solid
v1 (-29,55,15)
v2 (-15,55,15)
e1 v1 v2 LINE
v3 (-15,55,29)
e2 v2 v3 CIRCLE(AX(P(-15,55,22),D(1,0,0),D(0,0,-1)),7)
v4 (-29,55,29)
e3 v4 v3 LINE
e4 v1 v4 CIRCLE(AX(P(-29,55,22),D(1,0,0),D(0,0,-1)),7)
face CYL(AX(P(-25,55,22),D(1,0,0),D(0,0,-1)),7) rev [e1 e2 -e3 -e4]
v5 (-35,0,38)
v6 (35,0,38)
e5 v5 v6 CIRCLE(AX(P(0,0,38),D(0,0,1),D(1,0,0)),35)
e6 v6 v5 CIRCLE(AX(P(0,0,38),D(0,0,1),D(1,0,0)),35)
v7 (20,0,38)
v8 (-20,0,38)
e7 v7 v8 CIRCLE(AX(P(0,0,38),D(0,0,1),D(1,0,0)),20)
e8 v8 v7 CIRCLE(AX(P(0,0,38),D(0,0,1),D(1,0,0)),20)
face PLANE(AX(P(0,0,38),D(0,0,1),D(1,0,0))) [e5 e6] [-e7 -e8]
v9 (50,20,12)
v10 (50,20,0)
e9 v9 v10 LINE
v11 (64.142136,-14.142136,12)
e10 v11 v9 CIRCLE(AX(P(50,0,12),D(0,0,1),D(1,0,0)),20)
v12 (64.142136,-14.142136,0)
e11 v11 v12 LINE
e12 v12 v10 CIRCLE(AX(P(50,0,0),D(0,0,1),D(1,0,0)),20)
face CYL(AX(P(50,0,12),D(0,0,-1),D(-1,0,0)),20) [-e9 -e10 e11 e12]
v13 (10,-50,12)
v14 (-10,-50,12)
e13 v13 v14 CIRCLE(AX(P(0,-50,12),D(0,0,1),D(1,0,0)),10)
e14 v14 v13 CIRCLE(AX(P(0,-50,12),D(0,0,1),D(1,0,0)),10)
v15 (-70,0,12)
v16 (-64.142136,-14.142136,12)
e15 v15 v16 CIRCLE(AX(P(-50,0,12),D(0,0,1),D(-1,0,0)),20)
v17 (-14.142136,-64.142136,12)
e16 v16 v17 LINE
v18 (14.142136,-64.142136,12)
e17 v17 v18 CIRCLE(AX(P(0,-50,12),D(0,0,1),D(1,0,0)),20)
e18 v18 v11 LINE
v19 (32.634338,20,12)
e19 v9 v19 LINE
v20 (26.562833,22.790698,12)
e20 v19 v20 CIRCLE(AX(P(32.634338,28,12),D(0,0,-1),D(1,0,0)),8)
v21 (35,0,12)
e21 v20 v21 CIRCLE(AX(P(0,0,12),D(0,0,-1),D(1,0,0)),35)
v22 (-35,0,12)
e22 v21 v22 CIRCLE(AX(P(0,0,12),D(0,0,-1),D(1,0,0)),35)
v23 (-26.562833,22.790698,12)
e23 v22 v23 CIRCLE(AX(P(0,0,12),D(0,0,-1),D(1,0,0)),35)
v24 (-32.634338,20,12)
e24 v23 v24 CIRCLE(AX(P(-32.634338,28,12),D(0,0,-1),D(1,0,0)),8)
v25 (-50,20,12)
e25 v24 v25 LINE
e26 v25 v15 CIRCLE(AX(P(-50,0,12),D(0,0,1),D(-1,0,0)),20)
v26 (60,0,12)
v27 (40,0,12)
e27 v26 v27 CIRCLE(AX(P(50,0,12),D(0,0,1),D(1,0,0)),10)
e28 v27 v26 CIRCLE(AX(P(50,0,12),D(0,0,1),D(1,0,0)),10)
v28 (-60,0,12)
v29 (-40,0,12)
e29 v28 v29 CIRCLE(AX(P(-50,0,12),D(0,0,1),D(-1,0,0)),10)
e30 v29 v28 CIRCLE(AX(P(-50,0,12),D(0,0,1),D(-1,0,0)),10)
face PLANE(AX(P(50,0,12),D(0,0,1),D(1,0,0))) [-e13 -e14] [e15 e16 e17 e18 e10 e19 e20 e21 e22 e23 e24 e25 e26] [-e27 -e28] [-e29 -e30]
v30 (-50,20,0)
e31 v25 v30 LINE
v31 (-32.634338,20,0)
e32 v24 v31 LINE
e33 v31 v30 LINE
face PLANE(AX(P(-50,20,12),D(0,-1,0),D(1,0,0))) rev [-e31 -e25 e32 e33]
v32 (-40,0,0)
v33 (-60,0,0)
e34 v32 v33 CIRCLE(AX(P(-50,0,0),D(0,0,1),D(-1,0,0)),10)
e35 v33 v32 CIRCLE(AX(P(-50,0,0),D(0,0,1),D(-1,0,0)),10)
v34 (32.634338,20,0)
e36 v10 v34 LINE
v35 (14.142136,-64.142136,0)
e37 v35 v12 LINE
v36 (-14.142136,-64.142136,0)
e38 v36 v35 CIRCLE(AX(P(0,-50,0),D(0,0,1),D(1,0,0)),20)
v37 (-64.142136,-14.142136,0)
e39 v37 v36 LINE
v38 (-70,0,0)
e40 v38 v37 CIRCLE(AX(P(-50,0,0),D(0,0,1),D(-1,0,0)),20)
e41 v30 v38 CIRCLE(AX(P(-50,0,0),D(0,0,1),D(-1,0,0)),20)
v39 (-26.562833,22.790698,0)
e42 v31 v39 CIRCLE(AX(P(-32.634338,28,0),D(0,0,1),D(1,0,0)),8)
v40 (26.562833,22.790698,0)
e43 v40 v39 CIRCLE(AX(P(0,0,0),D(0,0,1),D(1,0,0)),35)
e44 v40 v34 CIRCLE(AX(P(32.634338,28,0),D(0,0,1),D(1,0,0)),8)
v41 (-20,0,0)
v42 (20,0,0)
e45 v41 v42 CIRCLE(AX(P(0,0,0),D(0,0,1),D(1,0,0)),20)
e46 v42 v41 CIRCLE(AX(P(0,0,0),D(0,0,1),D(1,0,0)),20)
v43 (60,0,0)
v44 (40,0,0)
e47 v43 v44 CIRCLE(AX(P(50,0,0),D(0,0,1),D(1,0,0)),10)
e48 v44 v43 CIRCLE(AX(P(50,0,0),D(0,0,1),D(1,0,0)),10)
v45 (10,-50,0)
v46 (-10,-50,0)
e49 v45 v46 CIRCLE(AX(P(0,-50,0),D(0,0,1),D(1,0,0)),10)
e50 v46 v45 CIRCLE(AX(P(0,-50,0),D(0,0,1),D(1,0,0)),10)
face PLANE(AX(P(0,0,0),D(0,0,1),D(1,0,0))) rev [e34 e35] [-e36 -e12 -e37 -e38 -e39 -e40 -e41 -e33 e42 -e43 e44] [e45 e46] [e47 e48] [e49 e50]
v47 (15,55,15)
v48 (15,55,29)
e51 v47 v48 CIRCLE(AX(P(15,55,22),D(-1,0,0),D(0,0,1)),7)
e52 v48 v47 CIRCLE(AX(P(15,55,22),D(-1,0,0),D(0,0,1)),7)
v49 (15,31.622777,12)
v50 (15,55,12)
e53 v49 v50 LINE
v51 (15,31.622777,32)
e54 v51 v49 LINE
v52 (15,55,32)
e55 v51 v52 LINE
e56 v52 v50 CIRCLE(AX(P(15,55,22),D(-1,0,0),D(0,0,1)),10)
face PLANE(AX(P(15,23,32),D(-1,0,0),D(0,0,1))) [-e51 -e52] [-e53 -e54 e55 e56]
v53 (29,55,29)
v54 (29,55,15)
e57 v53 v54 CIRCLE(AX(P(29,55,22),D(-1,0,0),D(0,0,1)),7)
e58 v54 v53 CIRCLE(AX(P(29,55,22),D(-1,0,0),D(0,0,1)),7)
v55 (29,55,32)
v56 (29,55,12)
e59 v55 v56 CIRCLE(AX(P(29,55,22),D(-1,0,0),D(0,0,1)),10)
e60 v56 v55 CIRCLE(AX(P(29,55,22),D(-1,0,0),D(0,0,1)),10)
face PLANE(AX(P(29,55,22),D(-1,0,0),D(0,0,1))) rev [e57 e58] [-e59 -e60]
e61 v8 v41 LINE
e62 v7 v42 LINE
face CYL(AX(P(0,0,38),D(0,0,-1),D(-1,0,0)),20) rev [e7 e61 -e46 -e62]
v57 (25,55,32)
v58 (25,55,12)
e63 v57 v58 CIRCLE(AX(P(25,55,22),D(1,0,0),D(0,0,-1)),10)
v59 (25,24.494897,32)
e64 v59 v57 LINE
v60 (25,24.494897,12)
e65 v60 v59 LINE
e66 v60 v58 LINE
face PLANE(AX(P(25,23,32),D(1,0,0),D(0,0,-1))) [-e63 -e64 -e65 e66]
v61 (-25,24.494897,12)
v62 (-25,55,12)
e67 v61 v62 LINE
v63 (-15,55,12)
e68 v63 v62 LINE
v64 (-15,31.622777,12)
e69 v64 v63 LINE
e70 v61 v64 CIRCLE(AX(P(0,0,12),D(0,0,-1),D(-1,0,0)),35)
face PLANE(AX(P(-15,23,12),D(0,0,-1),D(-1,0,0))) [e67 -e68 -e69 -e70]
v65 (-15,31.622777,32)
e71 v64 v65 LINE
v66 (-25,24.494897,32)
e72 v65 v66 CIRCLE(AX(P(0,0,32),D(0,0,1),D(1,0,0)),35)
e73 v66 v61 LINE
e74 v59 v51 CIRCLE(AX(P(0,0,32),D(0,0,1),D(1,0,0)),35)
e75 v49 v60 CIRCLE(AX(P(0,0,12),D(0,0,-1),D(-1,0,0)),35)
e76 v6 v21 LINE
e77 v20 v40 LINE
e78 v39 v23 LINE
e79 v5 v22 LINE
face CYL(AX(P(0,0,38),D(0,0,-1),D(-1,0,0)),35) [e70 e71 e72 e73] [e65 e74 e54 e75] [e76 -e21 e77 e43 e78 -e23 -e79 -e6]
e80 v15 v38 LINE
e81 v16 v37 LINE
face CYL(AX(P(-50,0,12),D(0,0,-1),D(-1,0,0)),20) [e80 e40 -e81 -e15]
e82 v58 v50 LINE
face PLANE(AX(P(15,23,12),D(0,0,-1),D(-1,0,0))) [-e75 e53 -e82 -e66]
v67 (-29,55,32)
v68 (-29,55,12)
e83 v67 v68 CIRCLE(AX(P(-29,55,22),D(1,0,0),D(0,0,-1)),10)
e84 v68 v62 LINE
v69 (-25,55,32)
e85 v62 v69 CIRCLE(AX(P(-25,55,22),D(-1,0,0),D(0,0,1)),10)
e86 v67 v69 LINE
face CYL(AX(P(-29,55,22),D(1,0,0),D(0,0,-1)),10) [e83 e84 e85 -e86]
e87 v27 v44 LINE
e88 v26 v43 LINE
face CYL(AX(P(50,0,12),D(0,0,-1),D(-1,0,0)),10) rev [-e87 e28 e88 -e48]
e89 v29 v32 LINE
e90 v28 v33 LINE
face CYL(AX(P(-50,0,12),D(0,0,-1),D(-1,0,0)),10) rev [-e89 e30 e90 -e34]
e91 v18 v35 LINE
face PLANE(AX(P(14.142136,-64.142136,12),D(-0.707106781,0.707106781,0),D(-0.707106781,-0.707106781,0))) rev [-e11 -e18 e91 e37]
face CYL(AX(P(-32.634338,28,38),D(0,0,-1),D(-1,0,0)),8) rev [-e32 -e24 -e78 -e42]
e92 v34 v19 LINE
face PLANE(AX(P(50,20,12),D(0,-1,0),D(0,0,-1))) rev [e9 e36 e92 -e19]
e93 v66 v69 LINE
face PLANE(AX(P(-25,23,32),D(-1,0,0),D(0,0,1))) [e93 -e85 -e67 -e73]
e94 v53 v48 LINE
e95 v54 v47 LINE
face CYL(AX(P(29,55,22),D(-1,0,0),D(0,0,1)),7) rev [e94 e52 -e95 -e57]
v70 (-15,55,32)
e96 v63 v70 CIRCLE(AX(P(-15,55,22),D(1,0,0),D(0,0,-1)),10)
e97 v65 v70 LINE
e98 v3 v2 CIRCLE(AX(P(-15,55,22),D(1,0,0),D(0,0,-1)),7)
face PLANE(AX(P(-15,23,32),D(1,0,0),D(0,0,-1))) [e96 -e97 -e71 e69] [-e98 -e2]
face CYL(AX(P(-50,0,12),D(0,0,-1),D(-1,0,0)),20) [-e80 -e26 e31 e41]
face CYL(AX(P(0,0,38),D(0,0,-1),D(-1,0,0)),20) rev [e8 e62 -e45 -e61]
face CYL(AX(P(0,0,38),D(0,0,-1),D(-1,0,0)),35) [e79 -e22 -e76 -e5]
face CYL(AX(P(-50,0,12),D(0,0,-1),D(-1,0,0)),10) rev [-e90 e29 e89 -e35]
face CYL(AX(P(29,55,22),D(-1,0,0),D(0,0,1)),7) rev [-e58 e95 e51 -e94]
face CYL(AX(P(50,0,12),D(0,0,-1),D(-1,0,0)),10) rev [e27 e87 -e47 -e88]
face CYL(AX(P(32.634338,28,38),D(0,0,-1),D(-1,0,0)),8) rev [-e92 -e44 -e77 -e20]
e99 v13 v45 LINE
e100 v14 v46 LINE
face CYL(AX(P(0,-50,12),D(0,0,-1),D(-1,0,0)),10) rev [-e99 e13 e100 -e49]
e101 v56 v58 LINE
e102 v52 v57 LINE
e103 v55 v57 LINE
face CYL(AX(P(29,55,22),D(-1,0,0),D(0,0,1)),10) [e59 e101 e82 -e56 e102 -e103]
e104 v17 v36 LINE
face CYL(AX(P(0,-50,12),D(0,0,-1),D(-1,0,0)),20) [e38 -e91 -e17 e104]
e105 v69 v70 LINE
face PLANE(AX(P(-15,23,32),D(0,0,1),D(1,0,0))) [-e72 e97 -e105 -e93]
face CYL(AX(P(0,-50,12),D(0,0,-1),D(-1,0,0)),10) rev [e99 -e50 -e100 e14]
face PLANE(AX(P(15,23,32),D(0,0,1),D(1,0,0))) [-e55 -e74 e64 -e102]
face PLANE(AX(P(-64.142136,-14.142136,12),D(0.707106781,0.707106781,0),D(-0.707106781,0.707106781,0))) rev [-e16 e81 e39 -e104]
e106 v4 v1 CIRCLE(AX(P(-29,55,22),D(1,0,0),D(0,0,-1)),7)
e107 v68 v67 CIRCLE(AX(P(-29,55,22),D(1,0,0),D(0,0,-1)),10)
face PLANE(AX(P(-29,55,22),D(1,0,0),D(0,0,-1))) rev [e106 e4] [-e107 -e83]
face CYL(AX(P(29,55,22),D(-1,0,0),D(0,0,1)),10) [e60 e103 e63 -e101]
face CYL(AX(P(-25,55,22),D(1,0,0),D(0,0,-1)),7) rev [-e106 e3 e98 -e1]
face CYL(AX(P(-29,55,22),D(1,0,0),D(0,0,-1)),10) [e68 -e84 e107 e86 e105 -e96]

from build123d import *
from build123d.topology import SkipClean

# Parameters (mm, degrees)
HUB_PROFILE_SKETCH_R     = 35
HUB_PROFILE_SKETCH_R_2   = 20
HUB_70_BORE_40_DEPTH     = 38
MOUNTING_FLANGE_SKETCH_R = 10
MOUNTING_FLANGE_DEPTH    = 12
FLANGE_HUB_FILLET_R8_R   = 8
CLEVIS_LUG_SKETCH_W      = 10
CLEVIS_LUG_SKETCH_H      = 20
CLEVIS_LUGS_DEPTH        = 32
LUG_BOSS_SKETCH_A_R      = 10
LUG_BOSS_SKETCH_A_R_2    = 7
LUG_BOSS_A_20_DEPTH      = 14
PIN_START                = -50
PIN_HOLE_SKETCH_R        = 7
PIN_HOLE_14_DEPTH        = 50
LUG_START                = -14
LUG_BOSS_SKETCH_B_R      = 10
LUG_BOSS_SKETCH_B_R_2    = 7
LUG_BOSS_B_20_DEPTH      = 14


with BuildPart() as part:
    # Hub Profile Sketch → Hub Ø70 Bore Ø40 (new body)
    with BuildSketch(Plane.XY):
        Circle(HUB_PROFILE_SKETCH_R)
        Circle(HUB_PROFILE_SKETCH_R_2, mode=Mode.SUBTRACT)
    extrude(amount=HUB_70_BORE_40_DEPTH)

    # Mounting Flange Sketch → Mounting Flange (add)
    with BuildSketch(Plane.XY):
        with BuildLine():
            Line((50, 20), (28.722813233, 20))
            ThreePointArc((28.722813233, 20), (0, -35), (-28.722813233, 20))
            Line((-28.722813233, 20), (-50, 20))
            ThreePointArc((-50, 20), (-68.47759065, 7.653668647), (-64.142135624, -14.142135624))
            Line((-64.142135624, -14.142135624), (-14.142135624, -64.142135624))
            ThreePointArc((-14.142135624, -64.142135624), (0, -70), (14.142135624, -64.142135624))
            Line((14.142135624, -64.142135624), (64.142135624, -14.142135624))
            ThreePointArc((64.142135624, -14.142135624), (68.47759065, 7.653668647), (50, 20))
        make_face()
        with Locations((50, 0)):
            Circle(MOUNTING_FLANGE_SKETCH_R, mode=Mode.SUBTRACT)
        with Locations((0, -50)):
            Circle(MOUNTING_FLANGE_SKETCH_R, mode=Mode.SUBTRACT)
        with Locations(Location((-50, 0, 0), (0, 0, 180))):
            Circle(MOUNTING_FLANGE_SKETCH_R, mode=Mode.SUBTRACT)
    extrude(amount=MOUNTING_FLANGE_DEPTH)

    # Flange Hub Fillet R8
    flange_hub_fillet_r8_edges = [part.edges().sort_by_distance(p)[0] for p in [
        (28.722813233, 20, 6),
        (-28.722813233, 20, 6),
    ]]
    fillet(flange_hub_fillet_r8_edges, radius=FLANGE_HUB_FILLET_R8_R)

    # Clevis Lug Sketch → Clevis Lugs (add)
    with BuildSketch(Plane(origin=(0, 55, 0), x_dir=(1, 0, 0), z_dir=(0, 1, 0))):
        with Locations((-20, -22)):
            Rectangle(CLEVIS_LUG_SKETCH_W, CLEVIS_LUG_SKETCH_H)
        with Locations((20, -22)):
            Rectangle(CLEVIS_LUG_SKETCH_W, CLEVIS_LUG_SKETCH_H)
    extrude(amount=-CLEVIS_LUGS_DEPTH)

    # Lug Boss Sketch A → Lug Boss A Ø20 (add)
    with BuildSketch(Plane.ZY.offset(-15)):
        with Locations((22, 55)):
            Circle(LUG_BOSS_SKETCH_A_R)
        with Locations((22, 55)):
            Circle(LUG_BOSS_SKETCH_A_R_2, mode=Mode.SUBTRACT)
    extrude(amount=-LUG_BOSS_A_20_DEPTH)

    # Pin Hole Sketch → Pin Hole Ø14 (cut)
    with SkipClean():  # the faces are left unmerged after this step: merging them gives an invalid solid
        with BuildSketch(Plane(origin=(25, 0, 0), x_dir=(0, 0, -1), z_dir=(1, 0, 0)).offset(PIN_START)):
            with Locations(Location((-22, 55, 0), (0, 0, 180))):
                Circle(PIN_HOLE_SKETCH_R)
        extrude(amount=PIN_HOLE_14_DEPTH, mode=Mode.SUBTRACT)

    # Lug Boss Sketch B → Lug Boss B Ø20 (add)
    with SkipClean():  # the faces are left unmerged after this step: merging them gives an invalid solid
        with BuildSketch(Plane(origin=(-15, 0, 0), x_dir=(0, 0, -1), z_dir=(1, 0, 0)).offset(LUG_START)):
            with Locations(Location((-22, 55, 0), (0, 0, 180))):
                Circle(LUG_BOSS_SKETCH_B_R)
            with Locations(Location((-22, 55, 0), (0, 0, 180))):
                Circle(LUG_BOSS_SKETCH_B_R_2, mode=Mode.SUBTRACT)
        extrude(amount=LUG_BOSS_B_20_DEPTH)


solid = part.part
